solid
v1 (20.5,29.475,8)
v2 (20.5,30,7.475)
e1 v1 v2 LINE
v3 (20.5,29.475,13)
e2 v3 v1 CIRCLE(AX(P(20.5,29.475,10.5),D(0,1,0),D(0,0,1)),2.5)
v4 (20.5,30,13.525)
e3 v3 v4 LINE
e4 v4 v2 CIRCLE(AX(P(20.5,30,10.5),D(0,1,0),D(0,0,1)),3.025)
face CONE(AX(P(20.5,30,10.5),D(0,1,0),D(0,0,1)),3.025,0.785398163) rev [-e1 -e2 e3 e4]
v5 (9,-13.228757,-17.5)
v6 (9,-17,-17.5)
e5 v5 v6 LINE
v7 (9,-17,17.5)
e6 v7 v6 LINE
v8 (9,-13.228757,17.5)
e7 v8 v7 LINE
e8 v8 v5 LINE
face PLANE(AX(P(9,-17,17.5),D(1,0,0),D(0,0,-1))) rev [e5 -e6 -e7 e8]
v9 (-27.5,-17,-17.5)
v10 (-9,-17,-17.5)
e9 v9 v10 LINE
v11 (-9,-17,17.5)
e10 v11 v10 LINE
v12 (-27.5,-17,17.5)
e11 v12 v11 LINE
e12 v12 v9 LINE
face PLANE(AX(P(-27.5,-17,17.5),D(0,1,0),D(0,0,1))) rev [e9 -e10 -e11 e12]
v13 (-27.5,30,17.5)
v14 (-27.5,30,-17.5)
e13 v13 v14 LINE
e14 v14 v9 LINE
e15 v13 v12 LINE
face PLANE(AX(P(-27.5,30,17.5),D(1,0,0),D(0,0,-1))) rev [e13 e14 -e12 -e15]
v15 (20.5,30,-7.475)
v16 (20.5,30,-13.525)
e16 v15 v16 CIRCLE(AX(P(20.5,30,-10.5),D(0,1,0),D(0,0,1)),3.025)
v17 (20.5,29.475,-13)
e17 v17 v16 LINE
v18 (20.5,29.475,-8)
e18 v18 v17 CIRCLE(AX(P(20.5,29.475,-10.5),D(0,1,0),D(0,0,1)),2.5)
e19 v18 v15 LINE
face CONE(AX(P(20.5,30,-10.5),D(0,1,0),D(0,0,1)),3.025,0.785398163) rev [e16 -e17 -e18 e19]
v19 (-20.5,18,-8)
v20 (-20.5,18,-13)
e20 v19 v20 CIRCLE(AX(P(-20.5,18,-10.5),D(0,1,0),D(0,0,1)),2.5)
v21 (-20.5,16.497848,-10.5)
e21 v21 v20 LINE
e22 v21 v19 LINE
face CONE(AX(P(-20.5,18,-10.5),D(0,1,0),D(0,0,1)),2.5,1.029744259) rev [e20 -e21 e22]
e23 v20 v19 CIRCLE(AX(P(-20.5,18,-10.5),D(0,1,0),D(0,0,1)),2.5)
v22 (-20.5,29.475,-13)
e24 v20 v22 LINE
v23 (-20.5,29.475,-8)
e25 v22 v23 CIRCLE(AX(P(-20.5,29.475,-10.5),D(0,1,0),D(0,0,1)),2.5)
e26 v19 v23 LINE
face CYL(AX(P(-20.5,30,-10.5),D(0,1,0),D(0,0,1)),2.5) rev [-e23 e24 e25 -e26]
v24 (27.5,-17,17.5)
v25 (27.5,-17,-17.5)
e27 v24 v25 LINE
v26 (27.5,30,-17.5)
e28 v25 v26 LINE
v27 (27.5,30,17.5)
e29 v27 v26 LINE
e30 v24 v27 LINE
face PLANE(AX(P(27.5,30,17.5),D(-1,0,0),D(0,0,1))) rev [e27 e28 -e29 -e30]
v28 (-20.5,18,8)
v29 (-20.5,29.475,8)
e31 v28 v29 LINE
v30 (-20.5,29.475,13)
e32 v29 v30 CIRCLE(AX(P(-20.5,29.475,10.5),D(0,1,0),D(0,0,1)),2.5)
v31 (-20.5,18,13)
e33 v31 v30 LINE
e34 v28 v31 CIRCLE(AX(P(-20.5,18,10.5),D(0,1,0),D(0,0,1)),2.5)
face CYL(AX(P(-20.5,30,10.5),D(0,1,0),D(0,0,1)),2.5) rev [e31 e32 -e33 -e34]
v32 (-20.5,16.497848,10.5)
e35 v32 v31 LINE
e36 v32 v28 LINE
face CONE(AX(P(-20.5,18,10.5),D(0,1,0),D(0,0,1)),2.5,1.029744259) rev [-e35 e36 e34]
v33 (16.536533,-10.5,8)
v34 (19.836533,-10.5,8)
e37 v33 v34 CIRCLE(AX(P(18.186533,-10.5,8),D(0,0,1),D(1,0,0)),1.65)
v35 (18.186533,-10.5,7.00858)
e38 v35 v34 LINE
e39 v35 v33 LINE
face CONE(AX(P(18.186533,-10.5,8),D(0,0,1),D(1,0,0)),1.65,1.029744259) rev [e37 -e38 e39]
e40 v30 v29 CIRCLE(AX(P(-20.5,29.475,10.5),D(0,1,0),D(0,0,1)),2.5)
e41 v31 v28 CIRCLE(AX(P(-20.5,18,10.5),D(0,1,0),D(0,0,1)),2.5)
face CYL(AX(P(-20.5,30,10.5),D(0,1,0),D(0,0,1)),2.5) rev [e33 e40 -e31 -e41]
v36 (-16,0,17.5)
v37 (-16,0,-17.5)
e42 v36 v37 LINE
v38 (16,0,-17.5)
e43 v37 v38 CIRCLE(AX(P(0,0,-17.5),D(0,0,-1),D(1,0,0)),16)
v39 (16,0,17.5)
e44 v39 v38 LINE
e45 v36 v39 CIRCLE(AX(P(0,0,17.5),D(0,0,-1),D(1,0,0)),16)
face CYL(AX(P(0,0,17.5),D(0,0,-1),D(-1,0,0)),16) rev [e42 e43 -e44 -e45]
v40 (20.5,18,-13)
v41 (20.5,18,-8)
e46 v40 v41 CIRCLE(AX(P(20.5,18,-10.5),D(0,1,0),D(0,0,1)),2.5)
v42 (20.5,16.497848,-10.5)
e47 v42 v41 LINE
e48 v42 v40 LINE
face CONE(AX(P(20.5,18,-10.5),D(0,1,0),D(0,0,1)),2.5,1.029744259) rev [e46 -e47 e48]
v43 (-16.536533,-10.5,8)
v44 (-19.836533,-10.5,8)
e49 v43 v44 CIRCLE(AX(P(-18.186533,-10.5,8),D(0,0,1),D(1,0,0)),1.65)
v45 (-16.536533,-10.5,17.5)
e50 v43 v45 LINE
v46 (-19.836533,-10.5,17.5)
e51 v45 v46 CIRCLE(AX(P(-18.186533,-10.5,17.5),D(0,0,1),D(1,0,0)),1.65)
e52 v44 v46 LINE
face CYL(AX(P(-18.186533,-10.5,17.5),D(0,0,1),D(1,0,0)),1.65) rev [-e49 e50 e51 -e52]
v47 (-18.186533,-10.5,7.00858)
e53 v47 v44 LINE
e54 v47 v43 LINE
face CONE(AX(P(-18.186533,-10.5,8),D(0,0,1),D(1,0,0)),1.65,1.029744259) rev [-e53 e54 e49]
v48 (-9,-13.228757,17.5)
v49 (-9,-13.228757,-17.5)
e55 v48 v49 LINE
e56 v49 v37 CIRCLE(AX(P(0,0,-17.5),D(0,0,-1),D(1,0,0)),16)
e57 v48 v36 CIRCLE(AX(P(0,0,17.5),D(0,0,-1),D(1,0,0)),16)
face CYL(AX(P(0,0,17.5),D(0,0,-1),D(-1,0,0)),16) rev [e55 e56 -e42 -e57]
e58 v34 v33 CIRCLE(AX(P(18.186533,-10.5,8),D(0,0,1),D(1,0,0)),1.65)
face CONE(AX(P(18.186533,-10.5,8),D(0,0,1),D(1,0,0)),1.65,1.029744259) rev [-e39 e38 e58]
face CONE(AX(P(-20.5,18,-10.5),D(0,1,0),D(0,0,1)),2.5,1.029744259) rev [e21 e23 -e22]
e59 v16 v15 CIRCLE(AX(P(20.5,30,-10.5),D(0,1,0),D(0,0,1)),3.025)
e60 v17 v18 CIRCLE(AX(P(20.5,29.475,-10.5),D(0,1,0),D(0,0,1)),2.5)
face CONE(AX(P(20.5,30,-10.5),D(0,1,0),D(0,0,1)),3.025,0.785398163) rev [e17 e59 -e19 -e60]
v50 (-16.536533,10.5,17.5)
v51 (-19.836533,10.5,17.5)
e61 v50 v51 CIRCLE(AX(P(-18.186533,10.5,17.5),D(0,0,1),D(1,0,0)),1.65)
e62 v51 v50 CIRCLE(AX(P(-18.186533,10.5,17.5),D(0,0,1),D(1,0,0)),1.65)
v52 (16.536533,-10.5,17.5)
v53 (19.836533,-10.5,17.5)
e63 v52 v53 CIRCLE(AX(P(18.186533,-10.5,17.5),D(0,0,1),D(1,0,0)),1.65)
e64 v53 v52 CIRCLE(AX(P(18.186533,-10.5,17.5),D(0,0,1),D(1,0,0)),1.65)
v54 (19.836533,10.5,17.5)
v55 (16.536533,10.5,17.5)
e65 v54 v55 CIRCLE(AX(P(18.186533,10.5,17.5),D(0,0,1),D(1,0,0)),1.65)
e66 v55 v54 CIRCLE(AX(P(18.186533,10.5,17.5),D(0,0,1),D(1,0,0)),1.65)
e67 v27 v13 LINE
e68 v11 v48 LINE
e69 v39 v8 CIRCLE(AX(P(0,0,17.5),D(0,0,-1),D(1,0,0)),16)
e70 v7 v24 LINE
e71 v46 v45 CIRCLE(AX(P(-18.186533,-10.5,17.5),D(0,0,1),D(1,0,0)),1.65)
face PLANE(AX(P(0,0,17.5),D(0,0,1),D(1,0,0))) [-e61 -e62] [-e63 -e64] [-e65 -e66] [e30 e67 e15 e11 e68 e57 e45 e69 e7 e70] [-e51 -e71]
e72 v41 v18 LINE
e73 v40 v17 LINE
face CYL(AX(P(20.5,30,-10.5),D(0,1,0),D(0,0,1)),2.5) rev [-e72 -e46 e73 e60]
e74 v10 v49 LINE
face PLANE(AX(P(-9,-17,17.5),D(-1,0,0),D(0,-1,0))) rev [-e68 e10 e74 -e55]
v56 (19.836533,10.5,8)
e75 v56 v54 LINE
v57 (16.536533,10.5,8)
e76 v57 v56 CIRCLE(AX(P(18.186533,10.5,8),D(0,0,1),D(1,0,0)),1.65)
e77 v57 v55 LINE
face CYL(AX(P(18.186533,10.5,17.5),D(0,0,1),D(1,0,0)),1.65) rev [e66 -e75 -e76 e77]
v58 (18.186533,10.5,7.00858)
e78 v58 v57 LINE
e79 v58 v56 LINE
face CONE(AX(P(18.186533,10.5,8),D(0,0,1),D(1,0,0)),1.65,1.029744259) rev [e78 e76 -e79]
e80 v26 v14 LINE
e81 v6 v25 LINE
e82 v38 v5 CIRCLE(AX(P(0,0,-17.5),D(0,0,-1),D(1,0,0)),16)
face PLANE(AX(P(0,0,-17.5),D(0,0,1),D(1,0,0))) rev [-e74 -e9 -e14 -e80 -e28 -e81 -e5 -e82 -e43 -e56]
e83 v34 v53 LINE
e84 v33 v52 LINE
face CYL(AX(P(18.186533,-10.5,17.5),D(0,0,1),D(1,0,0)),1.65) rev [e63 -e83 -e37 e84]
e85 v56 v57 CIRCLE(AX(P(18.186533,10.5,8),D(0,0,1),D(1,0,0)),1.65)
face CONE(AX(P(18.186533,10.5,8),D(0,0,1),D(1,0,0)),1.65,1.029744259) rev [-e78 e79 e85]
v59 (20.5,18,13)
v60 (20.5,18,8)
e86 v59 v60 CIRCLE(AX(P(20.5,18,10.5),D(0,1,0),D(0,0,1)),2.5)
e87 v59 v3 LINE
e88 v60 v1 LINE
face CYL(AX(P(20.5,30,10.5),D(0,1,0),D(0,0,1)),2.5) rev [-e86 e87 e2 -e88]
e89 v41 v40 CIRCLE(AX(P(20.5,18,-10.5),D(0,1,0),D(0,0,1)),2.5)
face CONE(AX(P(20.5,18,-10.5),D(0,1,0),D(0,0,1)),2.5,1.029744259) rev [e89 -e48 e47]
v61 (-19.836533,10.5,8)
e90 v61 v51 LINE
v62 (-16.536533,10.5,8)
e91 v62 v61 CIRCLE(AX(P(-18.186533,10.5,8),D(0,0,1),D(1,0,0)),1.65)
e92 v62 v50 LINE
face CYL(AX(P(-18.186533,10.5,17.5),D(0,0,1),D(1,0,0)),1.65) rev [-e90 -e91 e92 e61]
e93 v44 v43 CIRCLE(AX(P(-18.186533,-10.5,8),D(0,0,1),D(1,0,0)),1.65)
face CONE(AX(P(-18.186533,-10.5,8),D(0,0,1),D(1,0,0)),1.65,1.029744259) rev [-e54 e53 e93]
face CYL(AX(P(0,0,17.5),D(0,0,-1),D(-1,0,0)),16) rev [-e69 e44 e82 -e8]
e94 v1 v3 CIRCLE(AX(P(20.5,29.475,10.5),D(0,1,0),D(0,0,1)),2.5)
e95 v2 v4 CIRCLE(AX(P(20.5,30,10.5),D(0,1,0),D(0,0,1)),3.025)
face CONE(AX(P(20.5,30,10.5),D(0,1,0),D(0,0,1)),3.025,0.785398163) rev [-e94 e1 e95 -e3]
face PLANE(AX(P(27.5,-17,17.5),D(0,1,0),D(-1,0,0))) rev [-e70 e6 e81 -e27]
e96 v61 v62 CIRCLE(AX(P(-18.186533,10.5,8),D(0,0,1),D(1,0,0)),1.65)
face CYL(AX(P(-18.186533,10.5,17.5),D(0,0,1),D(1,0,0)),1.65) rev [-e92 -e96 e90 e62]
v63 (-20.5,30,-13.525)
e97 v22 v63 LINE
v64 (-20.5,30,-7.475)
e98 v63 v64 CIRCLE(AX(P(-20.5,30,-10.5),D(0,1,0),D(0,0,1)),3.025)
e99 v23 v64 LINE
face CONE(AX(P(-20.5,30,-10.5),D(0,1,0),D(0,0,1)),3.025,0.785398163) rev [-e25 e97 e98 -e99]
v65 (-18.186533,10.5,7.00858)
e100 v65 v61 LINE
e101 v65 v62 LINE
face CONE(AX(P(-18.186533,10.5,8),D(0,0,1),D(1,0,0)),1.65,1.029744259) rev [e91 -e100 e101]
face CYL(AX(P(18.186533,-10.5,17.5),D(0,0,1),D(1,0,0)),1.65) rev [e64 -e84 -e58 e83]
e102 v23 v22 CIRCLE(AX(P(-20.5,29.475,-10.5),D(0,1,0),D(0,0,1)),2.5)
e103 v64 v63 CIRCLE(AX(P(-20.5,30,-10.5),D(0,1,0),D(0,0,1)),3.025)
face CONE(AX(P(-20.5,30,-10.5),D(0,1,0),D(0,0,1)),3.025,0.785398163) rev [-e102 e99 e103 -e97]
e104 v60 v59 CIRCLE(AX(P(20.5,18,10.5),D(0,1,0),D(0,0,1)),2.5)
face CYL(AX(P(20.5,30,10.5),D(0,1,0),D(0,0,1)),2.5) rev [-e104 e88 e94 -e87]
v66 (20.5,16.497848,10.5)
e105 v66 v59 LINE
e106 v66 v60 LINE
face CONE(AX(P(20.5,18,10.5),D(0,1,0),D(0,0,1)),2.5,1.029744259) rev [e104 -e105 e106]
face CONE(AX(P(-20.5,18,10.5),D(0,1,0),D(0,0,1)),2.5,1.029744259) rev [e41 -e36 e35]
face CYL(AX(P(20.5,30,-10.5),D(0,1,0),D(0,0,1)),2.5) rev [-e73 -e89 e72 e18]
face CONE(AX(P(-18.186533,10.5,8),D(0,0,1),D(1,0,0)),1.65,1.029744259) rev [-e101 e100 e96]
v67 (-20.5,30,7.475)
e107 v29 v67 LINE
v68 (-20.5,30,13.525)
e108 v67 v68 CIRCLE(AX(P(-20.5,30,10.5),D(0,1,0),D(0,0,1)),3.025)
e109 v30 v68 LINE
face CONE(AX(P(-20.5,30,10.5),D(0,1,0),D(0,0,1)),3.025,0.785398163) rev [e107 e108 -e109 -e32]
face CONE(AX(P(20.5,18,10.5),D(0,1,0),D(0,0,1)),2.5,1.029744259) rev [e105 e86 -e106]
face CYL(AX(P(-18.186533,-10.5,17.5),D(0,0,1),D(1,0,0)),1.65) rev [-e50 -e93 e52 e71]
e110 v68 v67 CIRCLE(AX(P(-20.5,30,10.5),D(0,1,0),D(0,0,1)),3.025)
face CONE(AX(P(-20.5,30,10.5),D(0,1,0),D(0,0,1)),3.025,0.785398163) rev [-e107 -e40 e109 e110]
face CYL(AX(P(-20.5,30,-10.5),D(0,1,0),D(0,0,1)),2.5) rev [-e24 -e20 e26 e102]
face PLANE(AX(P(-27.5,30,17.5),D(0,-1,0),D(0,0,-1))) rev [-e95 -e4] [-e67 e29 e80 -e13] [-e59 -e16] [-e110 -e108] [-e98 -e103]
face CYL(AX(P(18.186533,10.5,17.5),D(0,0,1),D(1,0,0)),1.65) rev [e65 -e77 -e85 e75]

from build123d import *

# Parameters (mm, degrees)
EXTRUDE_1_DEPTH              = 17.5
HOLE_WIZARD_M4_1_D           = 3.3
HOLE_WIZARD_M4_1_DEPTH       = 9.5
HOLE_WIZARD_M4_1_TIP         = 0.991420021
HOLE_WIZARD_M6_1_D           = 5
HOLE_WIZARD_M6_1_DEPTH       = 12
HOLE_WIZARD_M6_1_CSINK_D     = 6.05
HOLE_WIZARD_M6_1_CSINK_ANGLE = 90
HOLE_WIZARD_M6_1_TIP         = 1.502151548


with BuildPart() as part:
    # 草图1 → 凸台-拉伸1 (new, symmetric)
    with BuildSketch(Plane.XY):
        with BuildLine():
            Line((-27.5, 30), (27.5, 30))
            Line((27.5, 30), (27.5, -17))
            Line((27.5, -17), (9, -17))
            Line((9, -17), (9, -13.228756555))
            ThreePointArc((9, -13.228756555), (0, 16), (-9, -13.228756555))
            Line((-9, -13.228756555), (-9, -17))
            Line((-9, -17), (-27.5, -17))
            Line((-27.5, -17), (-27.5, 30))
        make_face()
    extrude(amount=EXTRUDE_1_DEPTH, both=True)

    # M4 螺纹孔1
    with Locations(Plane.XY.offset(17.5)):
        with Locations((18.186533479, 10.5), (18.186533479, -10.5), (-18.186533479, -10.5), (-18.186533479, 10.5)):
            Hole(HOLE_WIZARD_M4_1_D / 2, depth=HOLE_WIZARD_M4_1_DEPTH)
            with Locations((0, 0, -(HOLE_WIZARD_M4_1_DEPTH + HOLE_WIZARD_M4_1_TIP / 2))):  # 118° drill point
                Cone(0, HOLE_WIZARD_M4_1_D / 2, HOLE_WIZARD_M4_1_TIP, mode=Mode.SUBTRACT)

    # M6 螺纹孔1
    with Locations(Plane(origin=(-20.5, 30, 10.5), x_dir=(0, 0, 1), z_dir=(0, 1, 0))):
        with Locations((0, 0), (-21, 0), (-21, 41), (0, 41)):
            CounterSinkHole(HOLE_WIZARD_M6_1_D / 2, HOLE_WIZARD_M6_1_CSINK_D / 2, depth=HOLE_WIZARD_M6_1_DEPTH, counter_sink_angle=HOLE_WIZARD_M6_1_CSINK_ANGLE)
            with Locations((0, 0, -(HOLE_WIZARD_M6_1_DEPTH + HOLE_WIZARD_M6_1_TIP / 2))):  # 118° drill point
                Cone(0, HOLE_WIZARD_M6_1_D / 2, HOLE_WIZARD_M6_1_TIP, mode=Mode.SUBTRACT)


solid = part.part
